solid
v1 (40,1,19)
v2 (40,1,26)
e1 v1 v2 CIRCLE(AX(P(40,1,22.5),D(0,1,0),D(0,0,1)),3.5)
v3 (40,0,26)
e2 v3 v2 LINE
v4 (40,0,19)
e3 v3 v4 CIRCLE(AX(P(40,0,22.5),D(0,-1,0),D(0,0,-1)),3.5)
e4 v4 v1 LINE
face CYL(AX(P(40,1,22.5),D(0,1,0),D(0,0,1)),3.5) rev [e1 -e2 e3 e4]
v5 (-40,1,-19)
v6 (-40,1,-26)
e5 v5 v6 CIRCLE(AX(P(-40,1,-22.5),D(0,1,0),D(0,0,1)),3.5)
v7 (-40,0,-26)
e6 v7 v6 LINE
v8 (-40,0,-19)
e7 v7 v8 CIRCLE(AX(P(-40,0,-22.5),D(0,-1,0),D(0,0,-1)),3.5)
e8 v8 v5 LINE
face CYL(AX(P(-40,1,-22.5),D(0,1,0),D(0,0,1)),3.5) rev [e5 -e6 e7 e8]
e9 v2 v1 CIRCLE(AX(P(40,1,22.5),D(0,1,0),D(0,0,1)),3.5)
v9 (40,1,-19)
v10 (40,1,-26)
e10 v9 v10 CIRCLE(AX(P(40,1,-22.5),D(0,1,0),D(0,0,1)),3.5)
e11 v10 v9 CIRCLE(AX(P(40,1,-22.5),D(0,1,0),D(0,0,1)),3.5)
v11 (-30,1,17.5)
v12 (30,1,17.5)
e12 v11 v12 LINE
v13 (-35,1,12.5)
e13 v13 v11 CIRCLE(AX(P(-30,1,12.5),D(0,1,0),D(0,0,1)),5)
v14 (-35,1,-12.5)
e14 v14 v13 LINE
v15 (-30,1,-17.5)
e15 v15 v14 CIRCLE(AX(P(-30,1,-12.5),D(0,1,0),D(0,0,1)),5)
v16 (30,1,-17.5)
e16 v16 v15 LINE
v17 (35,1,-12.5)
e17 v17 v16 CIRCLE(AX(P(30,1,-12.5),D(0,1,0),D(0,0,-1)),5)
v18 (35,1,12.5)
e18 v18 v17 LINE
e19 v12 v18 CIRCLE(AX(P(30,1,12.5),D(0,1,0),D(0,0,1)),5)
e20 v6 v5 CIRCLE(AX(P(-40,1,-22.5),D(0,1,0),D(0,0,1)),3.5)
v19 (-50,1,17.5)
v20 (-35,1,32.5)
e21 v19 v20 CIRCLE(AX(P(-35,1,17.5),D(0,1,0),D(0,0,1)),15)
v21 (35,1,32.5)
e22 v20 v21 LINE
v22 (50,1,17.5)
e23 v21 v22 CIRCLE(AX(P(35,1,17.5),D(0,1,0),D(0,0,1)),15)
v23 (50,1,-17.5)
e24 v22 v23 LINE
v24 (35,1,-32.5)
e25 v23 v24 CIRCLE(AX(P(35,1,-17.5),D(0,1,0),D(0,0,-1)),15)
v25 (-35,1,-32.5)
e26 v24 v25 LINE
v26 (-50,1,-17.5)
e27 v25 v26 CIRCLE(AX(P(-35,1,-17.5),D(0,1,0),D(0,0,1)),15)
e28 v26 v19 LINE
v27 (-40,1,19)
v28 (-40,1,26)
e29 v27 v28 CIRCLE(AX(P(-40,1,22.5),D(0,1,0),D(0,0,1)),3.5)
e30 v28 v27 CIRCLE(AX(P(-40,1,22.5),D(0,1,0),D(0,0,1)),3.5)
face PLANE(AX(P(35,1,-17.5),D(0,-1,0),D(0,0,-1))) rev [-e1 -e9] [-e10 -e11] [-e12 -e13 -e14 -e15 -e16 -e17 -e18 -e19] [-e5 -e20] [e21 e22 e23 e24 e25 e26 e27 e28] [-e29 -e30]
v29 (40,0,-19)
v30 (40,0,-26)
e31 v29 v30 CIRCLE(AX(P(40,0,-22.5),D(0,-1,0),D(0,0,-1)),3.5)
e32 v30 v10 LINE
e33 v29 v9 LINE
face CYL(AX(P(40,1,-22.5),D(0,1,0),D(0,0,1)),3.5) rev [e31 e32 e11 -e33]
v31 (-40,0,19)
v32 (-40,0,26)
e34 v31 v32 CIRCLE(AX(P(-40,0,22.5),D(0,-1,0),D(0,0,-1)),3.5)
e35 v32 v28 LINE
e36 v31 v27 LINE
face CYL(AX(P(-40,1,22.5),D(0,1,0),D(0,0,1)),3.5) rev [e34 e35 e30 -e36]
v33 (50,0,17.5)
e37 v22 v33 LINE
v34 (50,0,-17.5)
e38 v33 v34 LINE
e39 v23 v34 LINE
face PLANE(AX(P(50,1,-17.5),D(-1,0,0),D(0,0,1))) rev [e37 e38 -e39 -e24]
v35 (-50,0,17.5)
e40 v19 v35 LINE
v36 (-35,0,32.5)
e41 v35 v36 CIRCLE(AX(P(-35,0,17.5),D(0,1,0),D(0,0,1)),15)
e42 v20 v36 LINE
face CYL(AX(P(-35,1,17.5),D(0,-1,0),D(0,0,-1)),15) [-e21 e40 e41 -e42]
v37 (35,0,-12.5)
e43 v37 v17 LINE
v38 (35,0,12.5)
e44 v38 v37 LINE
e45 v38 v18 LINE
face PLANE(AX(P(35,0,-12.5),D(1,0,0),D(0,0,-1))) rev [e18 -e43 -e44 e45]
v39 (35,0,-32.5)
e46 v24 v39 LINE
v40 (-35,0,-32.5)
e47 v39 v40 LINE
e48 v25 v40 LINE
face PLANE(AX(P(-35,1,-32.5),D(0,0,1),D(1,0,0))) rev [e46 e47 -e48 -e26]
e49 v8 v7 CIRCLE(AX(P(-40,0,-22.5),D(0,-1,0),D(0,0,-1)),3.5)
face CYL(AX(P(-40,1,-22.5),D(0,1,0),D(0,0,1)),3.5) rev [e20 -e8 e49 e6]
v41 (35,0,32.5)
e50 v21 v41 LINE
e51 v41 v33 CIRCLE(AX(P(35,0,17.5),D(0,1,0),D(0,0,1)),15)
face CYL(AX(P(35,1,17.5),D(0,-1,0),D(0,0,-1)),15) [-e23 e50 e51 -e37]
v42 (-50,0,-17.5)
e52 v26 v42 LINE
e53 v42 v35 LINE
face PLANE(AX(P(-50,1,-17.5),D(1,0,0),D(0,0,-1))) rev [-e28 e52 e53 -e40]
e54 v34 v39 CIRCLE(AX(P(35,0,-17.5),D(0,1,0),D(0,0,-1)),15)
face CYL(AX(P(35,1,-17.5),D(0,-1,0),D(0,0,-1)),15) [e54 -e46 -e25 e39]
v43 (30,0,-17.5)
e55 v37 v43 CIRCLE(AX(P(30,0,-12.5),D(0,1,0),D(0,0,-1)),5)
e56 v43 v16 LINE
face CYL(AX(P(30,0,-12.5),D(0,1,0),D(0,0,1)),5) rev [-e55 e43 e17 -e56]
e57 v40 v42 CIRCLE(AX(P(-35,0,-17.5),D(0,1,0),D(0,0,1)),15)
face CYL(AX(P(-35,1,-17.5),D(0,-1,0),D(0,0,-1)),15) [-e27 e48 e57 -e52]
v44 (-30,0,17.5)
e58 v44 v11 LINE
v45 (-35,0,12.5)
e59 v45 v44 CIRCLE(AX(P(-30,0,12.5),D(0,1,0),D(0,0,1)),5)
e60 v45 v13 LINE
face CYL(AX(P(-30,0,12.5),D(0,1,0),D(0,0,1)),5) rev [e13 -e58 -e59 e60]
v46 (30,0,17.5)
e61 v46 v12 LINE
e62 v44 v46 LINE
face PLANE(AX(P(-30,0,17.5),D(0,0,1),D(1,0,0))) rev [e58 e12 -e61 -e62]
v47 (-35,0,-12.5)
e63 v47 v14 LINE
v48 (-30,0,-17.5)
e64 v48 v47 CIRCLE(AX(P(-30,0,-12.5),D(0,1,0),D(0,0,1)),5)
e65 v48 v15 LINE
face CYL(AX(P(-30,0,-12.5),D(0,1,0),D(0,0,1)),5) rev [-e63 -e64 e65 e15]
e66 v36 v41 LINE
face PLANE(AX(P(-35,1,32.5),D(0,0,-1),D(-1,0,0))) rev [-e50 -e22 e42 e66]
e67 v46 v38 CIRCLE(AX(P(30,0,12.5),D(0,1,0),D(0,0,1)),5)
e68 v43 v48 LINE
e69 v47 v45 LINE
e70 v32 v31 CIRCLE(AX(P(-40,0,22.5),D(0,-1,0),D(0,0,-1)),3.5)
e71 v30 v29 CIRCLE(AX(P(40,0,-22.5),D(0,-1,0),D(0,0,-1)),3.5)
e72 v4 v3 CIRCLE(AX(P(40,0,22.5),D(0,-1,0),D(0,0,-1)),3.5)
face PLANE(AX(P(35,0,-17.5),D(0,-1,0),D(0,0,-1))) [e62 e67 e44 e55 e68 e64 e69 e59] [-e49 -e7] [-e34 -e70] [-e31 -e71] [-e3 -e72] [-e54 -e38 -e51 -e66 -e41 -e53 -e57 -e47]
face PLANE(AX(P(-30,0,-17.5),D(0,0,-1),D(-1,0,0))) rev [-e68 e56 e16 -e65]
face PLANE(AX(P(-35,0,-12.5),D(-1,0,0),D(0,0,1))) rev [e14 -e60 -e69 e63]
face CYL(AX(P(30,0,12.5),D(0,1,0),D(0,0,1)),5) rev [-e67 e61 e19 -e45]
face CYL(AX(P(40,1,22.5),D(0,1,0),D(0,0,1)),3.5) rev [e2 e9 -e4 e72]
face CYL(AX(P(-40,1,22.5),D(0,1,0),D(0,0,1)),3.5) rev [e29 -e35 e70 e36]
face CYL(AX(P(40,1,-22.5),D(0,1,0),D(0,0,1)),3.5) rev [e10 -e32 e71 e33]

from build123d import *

# Parameters (mm, degrees)
BOSS_EXTRUDE1_DEPTH  = 1
CUT_EXTRUDE1_DEPTH   = 60.642686056
HOLE1_D              = 7
LPATTERN1_COUNT      = 2
LPATTERN1_PITCH      = 80
LPATTERN1_COUNT_DIR2 = 2
LPATTERN1_PITCH_DIR2 = 45


with BuildPart() as part:
    # Sketch1 → Boss-Extrude1 (new body)
    with BuildSketch(Plane(origin=(0, 0, 0), x_dir=(1, 0, 0), z_dir=(0, 1, 0))):
        with BuildLine():
            Line((-35, 32.5), (35, 32.5))
            ThreePointArc((35, 32.5), (45.606601718, 28.106601718), (50, 17.5))
            Line((50, 17.5), (50, -17.5))
            ThreePointArc((50, -17.5), (45.606601718, -28.106601718), (35, -32.5))
            Line((35, -32.5), (-35, -32.5))
            ThreePointArc((-35, -32.5), (-45.606601718, -28.106601718), (-50, -17.5))
            Line((-50, -17.5), (-50, 17.5))
            ThreePointArc((-50, 17.5), (-45.606601718, 28.106601718), (-35, 32.5))
        make_face()
    extrude(amount=BOSS_EXTRUDE1_DEPTH)

    # Sketch2 → Cut-Extrude1 (cut, through all)
    with BuildSketch(Plane(origin=(0, 1, 0), x_dir=(1, 0, 0), z_dir=(0, 1, 0))):
        with BuildLine():
            Line((-30, 17.5), (30, 17.5))
            ThreePointArc((30, 17.5), (33.535533906, 16.035533906), (35, 12.5))
            Line((35, 12.5), (35, -12.5))
            ThreePointArc((35, -12.5), (33.535533906, -16.035533906), (30, -17.5))
            Line((30, -17.5), (-30, -17.5))
            ThreePointArc((-30, -17.5), (-33.535533906, -16.035533906), (-35, -12.5))
            Line((-35, -12.5), (-35, 12.5))
            ThreePointArc((-35, 12.5), (-33.535533906, 16.035533906), (-30, 17.5))
        make_face()
    extrude(amount=-CUT_EXTRUDE1_DEPTH, mode=Mode.SUBTRACT)

    # Hole1 (through all)
    with Locations(Plane(origin=(-40, 1, -22.5), x_dir=(0, 0, 1), z_dir=(0, 1, 0))):
        with Locations((0, 0)):
            hole1 = Hole(HOLE1_D / 2)

    # LPattern1: Hole1 2 × 2
    with Locations(*[(i * LPATTERN1_PITCH, 0, j * LPATTERN1_PITCH_DIR2) for i in range(LPATTERN1_COUNT) for j in range(LPATTERN1_COUNT_DIR2) if (i, j) != (0, 0)]):
        add(hole1, mode=Mode.SUBTRACT)


solid = part.part
